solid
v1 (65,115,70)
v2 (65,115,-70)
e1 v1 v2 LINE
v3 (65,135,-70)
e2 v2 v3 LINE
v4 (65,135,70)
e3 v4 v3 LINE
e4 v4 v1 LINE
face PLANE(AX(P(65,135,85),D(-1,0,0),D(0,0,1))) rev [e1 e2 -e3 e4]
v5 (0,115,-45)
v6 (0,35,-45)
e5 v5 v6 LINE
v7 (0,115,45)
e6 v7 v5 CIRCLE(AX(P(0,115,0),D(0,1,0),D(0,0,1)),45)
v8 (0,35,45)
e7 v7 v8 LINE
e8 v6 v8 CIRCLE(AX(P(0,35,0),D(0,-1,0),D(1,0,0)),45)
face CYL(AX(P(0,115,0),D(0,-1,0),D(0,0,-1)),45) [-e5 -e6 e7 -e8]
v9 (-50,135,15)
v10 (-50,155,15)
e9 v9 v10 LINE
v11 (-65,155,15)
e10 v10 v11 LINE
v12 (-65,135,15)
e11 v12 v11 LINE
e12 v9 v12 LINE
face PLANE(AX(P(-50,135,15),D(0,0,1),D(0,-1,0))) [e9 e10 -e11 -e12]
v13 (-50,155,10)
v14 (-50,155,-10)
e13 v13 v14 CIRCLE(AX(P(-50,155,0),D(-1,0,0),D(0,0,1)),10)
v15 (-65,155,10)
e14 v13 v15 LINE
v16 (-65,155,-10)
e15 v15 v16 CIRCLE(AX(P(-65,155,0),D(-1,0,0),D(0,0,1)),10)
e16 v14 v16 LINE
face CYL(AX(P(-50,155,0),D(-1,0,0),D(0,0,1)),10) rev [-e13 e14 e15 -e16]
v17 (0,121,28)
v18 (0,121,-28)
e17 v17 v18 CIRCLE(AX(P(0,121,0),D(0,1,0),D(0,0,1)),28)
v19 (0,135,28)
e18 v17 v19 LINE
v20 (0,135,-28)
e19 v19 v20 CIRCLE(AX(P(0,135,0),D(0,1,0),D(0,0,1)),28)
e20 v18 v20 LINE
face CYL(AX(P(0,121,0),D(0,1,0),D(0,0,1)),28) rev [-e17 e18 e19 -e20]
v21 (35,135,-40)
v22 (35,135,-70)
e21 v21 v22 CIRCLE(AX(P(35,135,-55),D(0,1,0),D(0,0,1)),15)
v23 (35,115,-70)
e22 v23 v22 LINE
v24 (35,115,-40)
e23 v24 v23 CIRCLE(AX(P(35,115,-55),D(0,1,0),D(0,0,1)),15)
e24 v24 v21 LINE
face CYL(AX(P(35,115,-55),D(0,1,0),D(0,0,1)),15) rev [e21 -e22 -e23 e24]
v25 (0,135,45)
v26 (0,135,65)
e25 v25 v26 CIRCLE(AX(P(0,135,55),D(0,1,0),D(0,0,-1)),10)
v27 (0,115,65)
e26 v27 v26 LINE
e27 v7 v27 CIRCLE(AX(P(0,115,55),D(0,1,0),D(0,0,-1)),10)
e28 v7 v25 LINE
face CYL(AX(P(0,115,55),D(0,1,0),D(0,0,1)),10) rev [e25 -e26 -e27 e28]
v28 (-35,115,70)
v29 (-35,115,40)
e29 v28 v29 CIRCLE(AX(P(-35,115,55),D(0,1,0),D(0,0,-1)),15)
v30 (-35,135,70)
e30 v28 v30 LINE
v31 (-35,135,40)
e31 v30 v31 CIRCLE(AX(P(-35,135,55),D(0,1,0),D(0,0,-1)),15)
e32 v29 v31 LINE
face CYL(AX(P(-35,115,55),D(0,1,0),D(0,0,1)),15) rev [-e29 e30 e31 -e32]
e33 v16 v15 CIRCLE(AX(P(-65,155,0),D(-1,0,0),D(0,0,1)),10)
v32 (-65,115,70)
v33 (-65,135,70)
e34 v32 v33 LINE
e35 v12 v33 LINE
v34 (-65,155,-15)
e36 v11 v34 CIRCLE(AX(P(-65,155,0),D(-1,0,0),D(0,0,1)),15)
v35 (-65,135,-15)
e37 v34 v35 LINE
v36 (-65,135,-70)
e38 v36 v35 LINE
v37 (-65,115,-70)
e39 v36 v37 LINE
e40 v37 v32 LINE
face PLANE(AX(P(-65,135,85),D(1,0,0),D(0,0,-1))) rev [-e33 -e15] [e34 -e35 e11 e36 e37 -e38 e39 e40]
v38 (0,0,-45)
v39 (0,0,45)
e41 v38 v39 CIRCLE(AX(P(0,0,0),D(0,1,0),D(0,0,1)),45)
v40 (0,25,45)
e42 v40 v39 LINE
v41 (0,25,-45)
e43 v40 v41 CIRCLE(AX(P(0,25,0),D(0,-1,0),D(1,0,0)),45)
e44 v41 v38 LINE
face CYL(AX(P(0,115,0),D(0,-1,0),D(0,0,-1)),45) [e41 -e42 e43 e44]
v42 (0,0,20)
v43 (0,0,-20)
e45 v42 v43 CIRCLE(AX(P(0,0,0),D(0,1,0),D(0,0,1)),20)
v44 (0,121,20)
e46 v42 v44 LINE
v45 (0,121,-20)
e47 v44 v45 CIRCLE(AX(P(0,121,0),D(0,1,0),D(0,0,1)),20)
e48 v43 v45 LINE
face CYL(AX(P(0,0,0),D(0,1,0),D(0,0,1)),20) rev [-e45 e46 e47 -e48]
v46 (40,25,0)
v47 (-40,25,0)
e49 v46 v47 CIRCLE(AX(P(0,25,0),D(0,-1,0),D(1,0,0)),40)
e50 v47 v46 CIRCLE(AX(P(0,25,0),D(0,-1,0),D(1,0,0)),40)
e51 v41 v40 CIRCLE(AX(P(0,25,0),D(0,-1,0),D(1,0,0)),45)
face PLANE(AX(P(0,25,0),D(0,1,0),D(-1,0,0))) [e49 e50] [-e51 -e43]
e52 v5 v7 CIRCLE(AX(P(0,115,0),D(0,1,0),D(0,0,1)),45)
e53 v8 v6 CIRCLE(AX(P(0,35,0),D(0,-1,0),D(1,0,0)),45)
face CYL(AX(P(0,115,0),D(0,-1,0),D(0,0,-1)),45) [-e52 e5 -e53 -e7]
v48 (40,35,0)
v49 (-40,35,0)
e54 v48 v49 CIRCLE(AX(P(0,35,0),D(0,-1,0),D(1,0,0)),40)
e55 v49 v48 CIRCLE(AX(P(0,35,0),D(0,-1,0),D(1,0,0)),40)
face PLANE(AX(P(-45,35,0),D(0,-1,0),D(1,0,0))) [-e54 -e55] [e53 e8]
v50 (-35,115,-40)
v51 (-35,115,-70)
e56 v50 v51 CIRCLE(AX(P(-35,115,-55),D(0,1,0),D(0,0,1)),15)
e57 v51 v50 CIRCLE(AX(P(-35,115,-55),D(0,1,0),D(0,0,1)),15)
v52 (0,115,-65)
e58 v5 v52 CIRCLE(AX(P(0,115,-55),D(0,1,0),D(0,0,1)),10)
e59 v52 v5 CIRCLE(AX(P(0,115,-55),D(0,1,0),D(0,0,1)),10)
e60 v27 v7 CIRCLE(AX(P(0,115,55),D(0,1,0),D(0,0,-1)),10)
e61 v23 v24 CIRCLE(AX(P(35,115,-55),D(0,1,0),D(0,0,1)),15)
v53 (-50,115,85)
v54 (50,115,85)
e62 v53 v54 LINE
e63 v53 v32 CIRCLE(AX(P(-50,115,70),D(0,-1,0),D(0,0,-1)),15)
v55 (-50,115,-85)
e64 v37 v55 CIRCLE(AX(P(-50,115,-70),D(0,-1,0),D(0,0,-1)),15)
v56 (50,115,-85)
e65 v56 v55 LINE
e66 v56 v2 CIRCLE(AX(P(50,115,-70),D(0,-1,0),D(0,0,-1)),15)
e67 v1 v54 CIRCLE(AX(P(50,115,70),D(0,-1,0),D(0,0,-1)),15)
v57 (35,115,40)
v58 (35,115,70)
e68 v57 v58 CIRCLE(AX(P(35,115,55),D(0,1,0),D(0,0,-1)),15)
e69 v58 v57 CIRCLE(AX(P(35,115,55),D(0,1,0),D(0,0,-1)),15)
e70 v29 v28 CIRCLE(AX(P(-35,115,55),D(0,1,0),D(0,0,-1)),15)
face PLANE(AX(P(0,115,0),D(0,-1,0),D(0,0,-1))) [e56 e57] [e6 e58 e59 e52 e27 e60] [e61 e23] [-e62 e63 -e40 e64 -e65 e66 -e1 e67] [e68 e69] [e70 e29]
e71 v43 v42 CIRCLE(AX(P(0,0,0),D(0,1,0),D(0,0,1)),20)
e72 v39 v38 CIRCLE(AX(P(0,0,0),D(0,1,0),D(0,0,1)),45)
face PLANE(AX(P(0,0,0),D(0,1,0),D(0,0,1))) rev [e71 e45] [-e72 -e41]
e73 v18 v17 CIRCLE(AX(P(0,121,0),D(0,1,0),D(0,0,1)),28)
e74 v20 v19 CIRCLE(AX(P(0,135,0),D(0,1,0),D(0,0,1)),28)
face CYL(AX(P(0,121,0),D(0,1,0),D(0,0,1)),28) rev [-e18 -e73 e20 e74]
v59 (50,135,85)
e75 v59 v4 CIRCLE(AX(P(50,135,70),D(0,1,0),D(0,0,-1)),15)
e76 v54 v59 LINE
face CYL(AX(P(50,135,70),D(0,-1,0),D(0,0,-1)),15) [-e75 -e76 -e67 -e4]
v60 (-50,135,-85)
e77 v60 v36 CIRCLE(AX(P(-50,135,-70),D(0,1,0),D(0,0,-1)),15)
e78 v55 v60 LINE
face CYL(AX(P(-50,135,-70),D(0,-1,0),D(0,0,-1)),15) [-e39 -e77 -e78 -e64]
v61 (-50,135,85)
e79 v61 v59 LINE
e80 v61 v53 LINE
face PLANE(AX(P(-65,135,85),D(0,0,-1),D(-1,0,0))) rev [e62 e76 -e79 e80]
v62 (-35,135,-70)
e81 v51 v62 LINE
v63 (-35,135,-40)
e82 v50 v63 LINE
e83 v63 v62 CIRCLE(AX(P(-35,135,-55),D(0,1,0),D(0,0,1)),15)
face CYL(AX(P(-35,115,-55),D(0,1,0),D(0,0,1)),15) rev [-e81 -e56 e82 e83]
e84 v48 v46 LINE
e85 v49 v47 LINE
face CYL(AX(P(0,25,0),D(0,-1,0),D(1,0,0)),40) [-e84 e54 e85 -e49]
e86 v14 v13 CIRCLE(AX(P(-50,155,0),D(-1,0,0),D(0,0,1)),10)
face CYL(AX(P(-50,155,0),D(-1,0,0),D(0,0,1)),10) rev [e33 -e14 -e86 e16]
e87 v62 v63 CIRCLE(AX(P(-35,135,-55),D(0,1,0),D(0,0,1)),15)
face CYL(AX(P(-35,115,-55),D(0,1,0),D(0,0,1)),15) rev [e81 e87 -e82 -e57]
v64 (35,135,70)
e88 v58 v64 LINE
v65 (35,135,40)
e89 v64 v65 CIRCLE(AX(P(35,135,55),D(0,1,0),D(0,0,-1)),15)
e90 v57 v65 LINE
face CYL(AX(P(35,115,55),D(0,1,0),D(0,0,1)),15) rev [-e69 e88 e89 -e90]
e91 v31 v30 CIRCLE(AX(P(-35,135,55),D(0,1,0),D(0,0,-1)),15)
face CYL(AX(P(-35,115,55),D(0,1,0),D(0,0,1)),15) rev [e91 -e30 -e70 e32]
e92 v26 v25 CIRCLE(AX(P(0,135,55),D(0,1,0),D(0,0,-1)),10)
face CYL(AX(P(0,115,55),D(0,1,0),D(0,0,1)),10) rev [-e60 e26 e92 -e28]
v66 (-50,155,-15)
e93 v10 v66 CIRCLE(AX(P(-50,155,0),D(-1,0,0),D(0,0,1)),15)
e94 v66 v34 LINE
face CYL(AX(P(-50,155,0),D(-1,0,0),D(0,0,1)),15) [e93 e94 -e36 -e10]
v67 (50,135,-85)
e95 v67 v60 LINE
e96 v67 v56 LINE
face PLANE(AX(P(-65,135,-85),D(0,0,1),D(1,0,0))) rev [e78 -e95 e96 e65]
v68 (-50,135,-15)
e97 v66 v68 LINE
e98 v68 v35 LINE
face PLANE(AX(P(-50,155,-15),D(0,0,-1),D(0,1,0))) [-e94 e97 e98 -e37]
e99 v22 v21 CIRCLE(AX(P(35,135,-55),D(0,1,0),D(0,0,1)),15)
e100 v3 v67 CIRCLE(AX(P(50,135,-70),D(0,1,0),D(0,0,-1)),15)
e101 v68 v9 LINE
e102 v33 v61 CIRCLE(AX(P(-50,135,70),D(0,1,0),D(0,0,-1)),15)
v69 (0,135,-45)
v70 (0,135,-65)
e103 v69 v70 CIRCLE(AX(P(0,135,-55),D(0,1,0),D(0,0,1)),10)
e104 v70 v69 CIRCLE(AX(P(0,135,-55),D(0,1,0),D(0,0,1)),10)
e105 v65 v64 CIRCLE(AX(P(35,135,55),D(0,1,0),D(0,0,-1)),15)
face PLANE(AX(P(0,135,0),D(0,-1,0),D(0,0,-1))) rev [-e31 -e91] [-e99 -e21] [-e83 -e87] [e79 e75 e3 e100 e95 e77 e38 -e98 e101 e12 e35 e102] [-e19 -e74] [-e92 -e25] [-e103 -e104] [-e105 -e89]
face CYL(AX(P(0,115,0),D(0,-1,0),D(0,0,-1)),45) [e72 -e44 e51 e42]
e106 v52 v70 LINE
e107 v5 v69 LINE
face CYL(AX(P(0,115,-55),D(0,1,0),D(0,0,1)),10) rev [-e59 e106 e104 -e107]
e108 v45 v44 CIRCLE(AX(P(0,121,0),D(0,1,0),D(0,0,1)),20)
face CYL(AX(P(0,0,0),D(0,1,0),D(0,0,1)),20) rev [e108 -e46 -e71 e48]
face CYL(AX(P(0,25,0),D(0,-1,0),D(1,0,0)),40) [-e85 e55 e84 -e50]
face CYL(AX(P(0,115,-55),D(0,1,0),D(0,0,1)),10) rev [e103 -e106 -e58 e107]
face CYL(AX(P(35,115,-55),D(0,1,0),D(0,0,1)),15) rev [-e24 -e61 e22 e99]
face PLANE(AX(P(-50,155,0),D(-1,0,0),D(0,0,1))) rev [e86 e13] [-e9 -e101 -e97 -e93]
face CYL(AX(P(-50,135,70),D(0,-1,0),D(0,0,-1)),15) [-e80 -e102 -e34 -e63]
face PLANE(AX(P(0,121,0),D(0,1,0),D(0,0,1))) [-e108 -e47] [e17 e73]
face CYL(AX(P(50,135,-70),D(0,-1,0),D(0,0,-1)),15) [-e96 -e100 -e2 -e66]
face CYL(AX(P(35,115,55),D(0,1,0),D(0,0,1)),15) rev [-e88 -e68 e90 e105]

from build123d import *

# Parameters (mm, degrees)
BARREL_SKETCH_R               = 45
HOUSING_BARREL_90_DEPTH       = 115
MOUNTING_FLANGE_SKETCH_W      = 130
MOUNTING_FLANGE_SKETCH_H      = 170
MOUNTING_FLANGE_170X130_DEPTH = 20
FLANGE_HOLES_SKETCH_R         = 15
FLANGE_HOLES_SKETCH_R_2       = 10
FLANGE_MOUNTING_HOLES_DEPTH   = 20
COUNTERBORE_SKETCH_R          = 28
COUNTERBORE_56_DEPTH          = 14
BORE_SKETCH_R                 = 20
BORE_40_DEPTH                 = 162.527087512
BARREL_GROOVE_SKETCH_W        = 45
BARREL_GROOVE_SKETCH_H        = 10
GROOVE_RING_SKETCH_W          = 40
GROOVE_RING_SKETCH_H          = 10
LIFTING_LUG_DEPTH             = 15
LUG_HOLE_SKETCH_R             = 10
LUG_HOLE_20_DEPTH             = 15
FLANGE_CORNER_FILLETS_R15_R   = 15
BOTTOM_RECESS_SKETCH_R        = 20
BOTTOM_RECESS_40_DEPTH        = 15


with BuildPart() as part:
    # Barrel Sketch → Housing Barrel Ø90 (new body)
    with BuildSketch(Plane(origin=(0, 0, 0), x_dir=(1, 0, 0), z_dir=(0, 1, 0))):
        with Locations(Location((0, 0, 0), (0, 0, 270))):
            Circle(BARREL_SKETCH_R)
    extrude(amount=HOUSING_BARREL_90_DEPTH)

    # Mounting Flange Sketch → Mounting Flange 170x130 (add)
    with BuildSketch(Plane(origin=(0, 115, 0), x_dir=(1, 0, 0), z_dir=(0, 1, 0))):
        Rectangle(MOUNTING_FLANGE_SKETCH_W, MOUNTING_FLANGE_SKETCH_H)
    extrude(amount=MOUNTING_FLANGE_170X130_DEPTH)

    # Flange Holes Sketch → Flange Mounting Holes (cut)
    with BuildSketch(Plane(origin=(0, 135, 0), x_dir=(1, 0, 0), z_dir=(0, 1, 0))):
        with Locations(Location((35, 55, 0), (0, 0, 270))):
            Circle(FLANGE_HOLES_SKETCH_R)
        with Locations(Location((0, 55, 0), (0, 0, 270))):
            Circle(FLANGE_HOLES_SKETCH_R_2)
        with Locations(Location((-35, 55, 0), (0, 0, 270))):
            Circle(FLANGE_HOLES_SKETCH_R)
        with Locations(Location((-35, -55, 0), (0, 0, 90))):
            Circle(FLANGE_HOLES_SKETCH_R)
        with Locations(Location((0, -55, 0), (0, 0, 89.999768226))):
            Circle(FLANGE_HOLES_SKETCH_R_2)
        with Locations(Location((35, -55, 0), (0, 0, 90))):
            Circle(FLANGE_HOLES_SKETCH_R)
    extrude(amount=-FLANGE_MOUNTING_HOLES_DEPTH, mode=Mode.SUBTRACT)

    # Counterbore Sketch → Counterbore Ø56 (cut)
    with BuildSketch(Plane(origin=(0, 135, 0), x_dir=(1, 0, 0), z_dir=(0, 1, 0))):
        with Locations(Location((0, 0, 0), (0, 0, 270))):
            Circle(COUNTERBORE_SKETCH_R)
    extrude(amount=-COUNTERBORE_56_DEPTH, mode=Mode.SUBTRACT)

    # Bore Sketch → Bore Ø40 (cut, through all)
    with BuildSketch(Plane(origin=(0, 121, 0), x_dir=(1, 0, 0), z_dir=(0, 1, 0))):
        with Locations(Location((0, 0, 0), (0, 0, 270))):
            Circle(BORE_SKETCH_R)
    extrude(amount=-BORE_40_DEPTH, mode=Mode.SUBTRACT)

    # Barrel Groove Sketch → Barrel Groove (revolve, cut)
    with BuildSketch(Plane.XY, mode=Mode.PRIVATE) as barrel_groove_sk:
        with Locations((-22.5, 30)):
            Rectangle(BARREL_GROOVE_SKETCH_W, BARREL_GROOVE_SKETCH_H)
    revolve(barrel_groove_sk.sketch.rotate(Axis((0, 25, 0), (0, 1, 0)), 90), axis=Axis((0, 25, 0), (0, 1, 0)), mode=Mode.SUBTRACT)


with BuildPart() as barrel_groove_piece_1:
    # of the separate pieces the step leaves, piece 1, a body of its own (barrel_groove_pieces)
    add(part.part.solids().sort_by_distance((-65, 115, 85))[0])



with BuildPart() as barrel_groove_piece_2:
    # of the separate pieces the step leaves, piece 2, a body of its own (barrel_groove_pieces)
    add(part.part.solids().sort_by_distance((0, 0, 45))[0])


with BuildPart() as barrel_groove_piece_1_1:
    add(barrel_groove_piece_1.part)

    add(barrel_groove_piece_2.part)  # Groove Ring merges Barrel Groove piece 2
    # Groove Ring Sketch → Groove Ring (revolve)
    with BuildSketch(Plane.XY, mode=Mode.PRIVATE) as groove_ring_sk:
        with Locations((-20, 30)):
            Rectangle(GROOVE_RING_SKETCH_W, GROOVE_RING_SKETCH_H)
    revolve(groove_ring_sk.sketch.rotate(Axis((0, 25, 0), (0, 1, 0)), 180), axis=Axis((0, 25, 0), (0, 1, 0)))

    # Lifting Lug Sketch → Lifting Lug (add)
    with BuildSketch(Plane.ZY.offset(65)):
        with BuildLine():
            Line((-15, 155), (-15, 135))
            Line((-15, 135), (15, 135))
            Line((15, 135), (15, 155))
            ThreePointArc((15, 155), (0, 170), (-15, 155))
        make_face()
    extrude(amount=-LIFTING_LUG_DEPTH)

    # Lug Hole Sketch → Lug Hole Ø20 (cut)
    with BuildSketch(Plane.ZY.offset(65)):
        with Locations((0, 155)):
            Circle(LUG_HOLE_SKETCH_R)
    extrude(amount=-LUG_HOLE_20_DEPTH, mode=Mode.SUBTRACT)

    # Flange Corner Fillets R15
    flange_corner_fillets_r15_edges = [barrel_groove_piece_1_1.edges().sort_by_distance(p)[0] for p in [
        (65, 125, 85),
        (65, 125, -85),
        (-65, 125, -85),
        (-65, 125, 85),
    ]]
    fillet(flange_corner_fillets_r15_edges, radius=FLANGE_CORNER_FILLETS_R15_R)

    # Bottom Recess Sketch → Bottom Recess Ø40 (cut)
    with BuildSketch(Plane.XZ.offset(-25)):
        with Locations(Location((0, 0, 0), (0, 0, 90))):
            Circle(BOTTOM_RECESS_SKETCH_R)
    extrude(amount=-BOTTOM_RECESS_40_DEPTH, mode=Mode.SUBTRACT)


solid = barrel_groove_piece_1_1.part
